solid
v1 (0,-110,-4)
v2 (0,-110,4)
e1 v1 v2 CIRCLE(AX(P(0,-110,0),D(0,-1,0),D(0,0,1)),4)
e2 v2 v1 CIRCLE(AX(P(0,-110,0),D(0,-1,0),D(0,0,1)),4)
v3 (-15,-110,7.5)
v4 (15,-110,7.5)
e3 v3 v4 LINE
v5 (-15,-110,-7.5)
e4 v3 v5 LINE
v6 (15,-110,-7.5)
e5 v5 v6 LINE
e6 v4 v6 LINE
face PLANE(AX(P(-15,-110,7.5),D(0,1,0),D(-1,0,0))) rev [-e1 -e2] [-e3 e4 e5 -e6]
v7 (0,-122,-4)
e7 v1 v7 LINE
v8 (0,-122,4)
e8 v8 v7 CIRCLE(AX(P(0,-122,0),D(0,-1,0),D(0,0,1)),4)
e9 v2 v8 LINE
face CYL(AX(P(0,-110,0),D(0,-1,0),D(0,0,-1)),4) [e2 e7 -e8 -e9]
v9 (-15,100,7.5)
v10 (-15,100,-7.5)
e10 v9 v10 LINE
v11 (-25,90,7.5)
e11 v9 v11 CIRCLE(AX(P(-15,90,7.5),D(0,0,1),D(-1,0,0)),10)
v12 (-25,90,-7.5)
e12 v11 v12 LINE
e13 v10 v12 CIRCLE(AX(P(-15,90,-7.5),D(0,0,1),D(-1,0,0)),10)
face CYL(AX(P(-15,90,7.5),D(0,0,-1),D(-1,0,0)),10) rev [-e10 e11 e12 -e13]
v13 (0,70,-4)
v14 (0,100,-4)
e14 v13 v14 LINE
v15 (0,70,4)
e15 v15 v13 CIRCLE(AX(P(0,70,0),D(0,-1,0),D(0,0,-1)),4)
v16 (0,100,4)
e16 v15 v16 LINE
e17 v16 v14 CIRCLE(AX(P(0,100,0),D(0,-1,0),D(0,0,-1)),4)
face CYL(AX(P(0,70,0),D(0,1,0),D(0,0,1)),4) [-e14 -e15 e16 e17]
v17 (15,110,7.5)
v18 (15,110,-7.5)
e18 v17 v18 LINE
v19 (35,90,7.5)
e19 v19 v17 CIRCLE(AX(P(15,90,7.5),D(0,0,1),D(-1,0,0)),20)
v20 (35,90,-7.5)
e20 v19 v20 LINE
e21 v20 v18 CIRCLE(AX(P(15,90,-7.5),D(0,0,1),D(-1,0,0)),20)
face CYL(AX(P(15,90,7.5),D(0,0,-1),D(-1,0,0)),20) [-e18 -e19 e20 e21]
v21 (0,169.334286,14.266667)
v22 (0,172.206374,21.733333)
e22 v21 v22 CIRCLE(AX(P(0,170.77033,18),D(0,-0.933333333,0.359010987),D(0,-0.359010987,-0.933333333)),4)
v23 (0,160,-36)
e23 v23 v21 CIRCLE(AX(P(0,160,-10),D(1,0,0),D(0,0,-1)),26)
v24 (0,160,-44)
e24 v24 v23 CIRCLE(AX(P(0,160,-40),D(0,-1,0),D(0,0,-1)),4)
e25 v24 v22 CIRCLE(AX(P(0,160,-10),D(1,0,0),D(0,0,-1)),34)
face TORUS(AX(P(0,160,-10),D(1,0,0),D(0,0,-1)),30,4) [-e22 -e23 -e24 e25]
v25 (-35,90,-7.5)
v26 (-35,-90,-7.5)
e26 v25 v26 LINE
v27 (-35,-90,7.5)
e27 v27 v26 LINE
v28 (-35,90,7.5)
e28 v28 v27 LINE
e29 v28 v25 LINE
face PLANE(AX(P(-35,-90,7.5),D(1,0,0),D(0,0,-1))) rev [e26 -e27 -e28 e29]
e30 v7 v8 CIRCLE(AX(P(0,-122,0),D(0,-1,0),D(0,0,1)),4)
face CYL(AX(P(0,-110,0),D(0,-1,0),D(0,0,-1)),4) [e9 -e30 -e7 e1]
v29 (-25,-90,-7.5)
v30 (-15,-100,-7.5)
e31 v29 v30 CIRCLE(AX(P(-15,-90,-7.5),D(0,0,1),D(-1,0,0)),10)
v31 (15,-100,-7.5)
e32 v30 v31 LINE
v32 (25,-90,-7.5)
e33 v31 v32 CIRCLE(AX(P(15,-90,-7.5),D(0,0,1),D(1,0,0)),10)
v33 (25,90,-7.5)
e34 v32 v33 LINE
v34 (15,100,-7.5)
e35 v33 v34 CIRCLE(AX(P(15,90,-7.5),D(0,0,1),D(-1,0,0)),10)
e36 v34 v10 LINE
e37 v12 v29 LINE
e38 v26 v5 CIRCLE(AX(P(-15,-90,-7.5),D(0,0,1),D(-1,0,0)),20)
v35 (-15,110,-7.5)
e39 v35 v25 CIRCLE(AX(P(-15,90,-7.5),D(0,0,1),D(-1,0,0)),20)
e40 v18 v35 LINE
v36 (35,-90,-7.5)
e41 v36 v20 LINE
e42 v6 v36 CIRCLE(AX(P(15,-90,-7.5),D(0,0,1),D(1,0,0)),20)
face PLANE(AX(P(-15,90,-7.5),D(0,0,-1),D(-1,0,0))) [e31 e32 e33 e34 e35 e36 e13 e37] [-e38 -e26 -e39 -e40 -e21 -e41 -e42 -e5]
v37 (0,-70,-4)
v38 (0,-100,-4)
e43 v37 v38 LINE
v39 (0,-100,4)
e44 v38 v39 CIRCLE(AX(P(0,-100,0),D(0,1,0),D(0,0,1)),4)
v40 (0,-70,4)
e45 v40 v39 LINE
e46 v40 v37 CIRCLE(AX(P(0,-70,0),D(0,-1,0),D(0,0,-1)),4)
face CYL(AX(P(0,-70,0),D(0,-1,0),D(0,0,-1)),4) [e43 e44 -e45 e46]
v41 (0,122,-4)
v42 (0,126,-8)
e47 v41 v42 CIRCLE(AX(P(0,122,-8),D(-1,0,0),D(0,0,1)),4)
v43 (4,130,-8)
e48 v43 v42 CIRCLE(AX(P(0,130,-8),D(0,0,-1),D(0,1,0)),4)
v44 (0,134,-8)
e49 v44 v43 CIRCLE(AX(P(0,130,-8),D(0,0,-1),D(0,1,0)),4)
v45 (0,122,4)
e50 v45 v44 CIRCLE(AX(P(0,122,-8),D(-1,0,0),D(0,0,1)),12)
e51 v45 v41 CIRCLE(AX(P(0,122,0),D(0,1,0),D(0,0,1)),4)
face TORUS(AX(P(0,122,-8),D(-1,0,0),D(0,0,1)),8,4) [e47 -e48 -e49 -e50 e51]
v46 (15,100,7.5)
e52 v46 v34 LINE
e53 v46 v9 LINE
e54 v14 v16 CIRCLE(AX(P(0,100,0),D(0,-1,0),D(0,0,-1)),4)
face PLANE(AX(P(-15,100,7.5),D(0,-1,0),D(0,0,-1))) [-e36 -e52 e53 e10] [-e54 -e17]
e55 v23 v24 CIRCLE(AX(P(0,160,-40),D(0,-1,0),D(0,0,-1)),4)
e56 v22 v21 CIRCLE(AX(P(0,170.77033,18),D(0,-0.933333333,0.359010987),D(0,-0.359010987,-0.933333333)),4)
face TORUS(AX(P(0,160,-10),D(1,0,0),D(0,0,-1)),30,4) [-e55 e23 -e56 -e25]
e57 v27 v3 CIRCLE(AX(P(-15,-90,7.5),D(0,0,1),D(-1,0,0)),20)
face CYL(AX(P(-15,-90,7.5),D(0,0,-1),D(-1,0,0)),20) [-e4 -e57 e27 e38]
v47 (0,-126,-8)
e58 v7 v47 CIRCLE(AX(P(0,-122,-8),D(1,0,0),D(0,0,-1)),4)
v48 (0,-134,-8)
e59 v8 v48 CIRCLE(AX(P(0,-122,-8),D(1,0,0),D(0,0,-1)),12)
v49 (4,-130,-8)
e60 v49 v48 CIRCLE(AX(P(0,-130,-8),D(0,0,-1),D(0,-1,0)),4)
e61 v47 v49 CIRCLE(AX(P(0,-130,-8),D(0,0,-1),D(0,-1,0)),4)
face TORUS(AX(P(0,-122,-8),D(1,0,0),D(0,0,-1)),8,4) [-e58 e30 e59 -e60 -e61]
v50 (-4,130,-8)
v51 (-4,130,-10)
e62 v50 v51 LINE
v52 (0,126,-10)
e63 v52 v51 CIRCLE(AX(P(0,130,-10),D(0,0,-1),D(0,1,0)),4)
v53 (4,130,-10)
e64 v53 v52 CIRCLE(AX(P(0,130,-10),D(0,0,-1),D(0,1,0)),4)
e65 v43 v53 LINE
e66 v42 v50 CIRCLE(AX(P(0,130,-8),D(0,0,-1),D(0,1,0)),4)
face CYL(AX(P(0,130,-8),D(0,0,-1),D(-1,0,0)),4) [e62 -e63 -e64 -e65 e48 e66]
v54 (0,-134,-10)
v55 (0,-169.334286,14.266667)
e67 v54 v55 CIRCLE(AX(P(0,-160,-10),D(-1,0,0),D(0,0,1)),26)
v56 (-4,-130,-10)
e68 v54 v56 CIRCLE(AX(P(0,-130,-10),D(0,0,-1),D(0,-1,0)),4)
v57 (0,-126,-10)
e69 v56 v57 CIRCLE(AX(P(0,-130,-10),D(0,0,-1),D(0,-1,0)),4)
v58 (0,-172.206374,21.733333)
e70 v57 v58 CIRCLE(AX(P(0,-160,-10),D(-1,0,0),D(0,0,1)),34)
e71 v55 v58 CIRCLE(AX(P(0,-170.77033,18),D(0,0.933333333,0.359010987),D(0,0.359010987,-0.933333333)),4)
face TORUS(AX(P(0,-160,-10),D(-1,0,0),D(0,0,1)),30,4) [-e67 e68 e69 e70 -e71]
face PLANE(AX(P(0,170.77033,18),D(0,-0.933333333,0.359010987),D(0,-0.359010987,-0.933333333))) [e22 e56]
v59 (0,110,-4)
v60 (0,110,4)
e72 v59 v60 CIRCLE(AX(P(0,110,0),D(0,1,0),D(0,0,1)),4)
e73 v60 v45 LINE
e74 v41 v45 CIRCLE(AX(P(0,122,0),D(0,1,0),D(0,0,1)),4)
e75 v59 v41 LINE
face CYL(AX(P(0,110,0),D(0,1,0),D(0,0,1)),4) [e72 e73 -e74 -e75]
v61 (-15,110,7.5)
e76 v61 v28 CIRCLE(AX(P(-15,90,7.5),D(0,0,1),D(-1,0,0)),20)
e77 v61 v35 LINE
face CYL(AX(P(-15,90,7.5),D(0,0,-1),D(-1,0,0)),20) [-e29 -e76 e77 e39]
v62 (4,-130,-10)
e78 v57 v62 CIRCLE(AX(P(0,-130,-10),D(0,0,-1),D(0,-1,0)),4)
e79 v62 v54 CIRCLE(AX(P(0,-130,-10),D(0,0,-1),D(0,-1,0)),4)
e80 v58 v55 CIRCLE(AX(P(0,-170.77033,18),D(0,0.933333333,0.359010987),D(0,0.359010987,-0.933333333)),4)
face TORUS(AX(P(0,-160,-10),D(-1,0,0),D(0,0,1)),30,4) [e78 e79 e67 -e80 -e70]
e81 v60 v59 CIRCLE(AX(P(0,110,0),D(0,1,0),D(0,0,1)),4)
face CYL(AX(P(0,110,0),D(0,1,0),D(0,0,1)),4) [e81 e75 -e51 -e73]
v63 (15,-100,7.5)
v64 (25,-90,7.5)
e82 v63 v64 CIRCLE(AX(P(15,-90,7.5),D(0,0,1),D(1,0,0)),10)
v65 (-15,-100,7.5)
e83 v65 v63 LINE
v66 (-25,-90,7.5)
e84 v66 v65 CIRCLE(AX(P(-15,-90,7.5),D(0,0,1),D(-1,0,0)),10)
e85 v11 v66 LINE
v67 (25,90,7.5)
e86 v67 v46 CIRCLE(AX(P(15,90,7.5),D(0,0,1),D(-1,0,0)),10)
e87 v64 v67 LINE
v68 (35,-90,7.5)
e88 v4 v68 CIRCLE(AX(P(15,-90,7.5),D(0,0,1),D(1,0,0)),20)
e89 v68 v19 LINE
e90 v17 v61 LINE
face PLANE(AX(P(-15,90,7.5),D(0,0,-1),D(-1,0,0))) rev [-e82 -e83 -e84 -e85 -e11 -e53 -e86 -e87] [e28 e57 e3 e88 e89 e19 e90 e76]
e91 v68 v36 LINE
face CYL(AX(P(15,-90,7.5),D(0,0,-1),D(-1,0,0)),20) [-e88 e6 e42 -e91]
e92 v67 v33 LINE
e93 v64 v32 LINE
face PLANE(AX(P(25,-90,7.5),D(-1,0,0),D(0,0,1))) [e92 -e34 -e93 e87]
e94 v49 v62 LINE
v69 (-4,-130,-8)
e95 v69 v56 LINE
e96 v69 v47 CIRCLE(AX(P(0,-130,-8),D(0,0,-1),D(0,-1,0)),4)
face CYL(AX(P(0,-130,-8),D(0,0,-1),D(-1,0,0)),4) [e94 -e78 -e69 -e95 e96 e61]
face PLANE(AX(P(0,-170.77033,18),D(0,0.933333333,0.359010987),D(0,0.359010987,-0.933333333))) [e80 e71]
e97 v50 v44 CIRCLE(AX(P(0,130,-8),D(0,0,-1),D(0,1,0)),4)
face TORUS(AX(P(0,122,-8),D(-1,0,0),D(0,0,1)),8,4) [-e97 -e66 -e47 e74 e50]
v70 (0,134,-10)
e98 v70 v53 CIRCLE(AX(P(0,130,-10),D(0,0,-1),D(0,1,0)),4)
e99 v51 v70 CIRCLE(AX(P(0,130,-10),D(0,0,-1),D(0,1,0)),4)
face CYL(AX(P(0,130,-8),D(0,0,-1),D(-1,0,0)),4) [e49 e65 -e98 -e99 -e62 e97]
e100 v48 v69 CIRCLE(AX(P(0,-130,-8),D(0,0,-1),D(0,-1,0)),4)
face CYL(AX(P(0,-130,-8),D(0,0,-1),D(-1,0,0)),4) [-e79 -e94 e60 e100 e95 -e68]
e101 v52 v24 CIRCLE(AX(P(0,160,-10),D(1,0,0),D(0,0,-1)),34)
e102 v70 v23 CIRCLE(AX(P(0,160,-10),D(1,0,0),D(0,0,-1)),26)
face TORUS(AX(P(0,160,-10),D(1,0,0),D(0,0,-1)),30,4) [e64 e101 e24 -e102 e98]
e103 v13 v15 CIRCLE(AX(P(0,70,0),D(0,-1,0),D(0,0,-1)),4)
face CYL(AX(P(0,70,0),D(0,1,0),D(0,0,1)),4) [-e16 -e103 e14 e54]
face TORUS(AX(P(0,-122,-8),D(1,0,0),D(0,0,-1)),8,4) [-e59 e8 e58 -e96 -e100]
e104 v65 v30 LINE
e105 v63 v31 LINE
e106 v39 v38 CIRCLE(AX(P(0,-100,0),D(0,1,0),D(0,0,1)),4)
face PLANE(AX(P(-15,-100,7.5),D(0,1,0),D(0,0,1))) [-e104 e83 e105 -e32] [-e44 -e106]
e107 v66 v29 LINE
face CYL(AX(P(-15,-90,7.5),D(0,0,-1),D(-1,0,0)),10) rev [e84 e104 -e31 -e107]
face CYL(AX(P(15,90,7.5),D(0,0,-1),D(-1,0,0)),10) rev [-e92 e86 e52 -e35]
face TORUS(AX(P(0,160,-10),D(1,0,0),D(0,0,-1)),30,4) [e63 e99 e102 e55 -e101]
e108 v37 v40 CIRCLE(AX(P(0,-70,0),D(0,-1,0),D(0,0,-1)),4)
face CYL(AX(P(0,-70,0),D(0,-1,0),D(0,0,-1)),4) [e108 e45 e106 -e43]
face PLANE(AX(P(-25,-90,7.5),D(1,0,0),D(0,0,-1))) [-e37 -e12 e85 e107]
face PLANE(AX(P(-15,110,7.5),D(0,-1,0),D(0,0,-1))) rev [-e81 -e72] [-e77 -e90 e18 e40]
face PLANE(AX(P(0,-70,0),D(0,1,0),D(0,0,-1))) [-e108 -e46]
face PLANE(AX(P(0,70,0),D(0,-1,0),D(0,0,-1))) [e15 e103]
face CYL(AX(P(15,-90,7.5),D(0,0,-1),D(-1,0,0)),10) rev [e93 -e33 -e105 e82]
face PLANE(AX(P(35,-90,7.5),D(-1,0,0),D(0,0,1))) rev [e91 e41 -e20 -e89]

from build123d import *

# Parameters (mm, degrees)
EXTRUDE_1_DEPTH = 7.5
SKETCH_6_R      = 4
SKETCH_7_R      = 4
EXTRUDE_2_DEPTH = 30


with BuildPart() as part:
    # 草图4 → 凸台-拉伸1 (new, symmetric)
    with BuildSketch(Plane.XY):
        with BuildLine():
            Line((-15, 110), (15, 110))
            ThreePointArc((15, 110), (29.142135624, 104.142135624), (35, 90))
            Line((35, 90), (35, -90))
            ThreePointArc((35, -90), (29.142135624, -104.142135624), (15, -110))
            Line((15, -110), (-15, -110))
            ThreePointArc((-15, -110), (-29.142135624, -104.142135624), (-35, -90))
            Line((-35, -90), (-35, 90))
            ThreePointArc((-35, 90), (-29.142135624, 104.142135624), (-15, 110))
        make_face()
        with BuildLine():
            Line((-15, -100), (15, -100))
            ThreePointArc((15, -100), (22.071067812, -97.071067812), (25, -90))
            Line((25, -90), (25, 90))
            ThreePointArc((25, 90), (22.071067812, 97.071067812), (15, 100))
            Line((15, 100), (-15, 100))
            ThreePointArc((-15, 100), (-22.071067812, 97.071067812), (-25, 90))
            Line((-25, 90), (-25, -90))
            ThreePointArc((-25, -90), (-22.071067812, -97.071067812), (-15, -100))
        make_face(mode=Mode.SUBTRACT)
    extrude(amount=EXTRUDE_1_DEPTH, both=True)

    # 扫描1: sweep along a path in 草图5
    with BuildLine(Plane(origin=(0, 0, 0), x_dir=(0, 0, -1), z_dir=(1, 0, 0))) as sweep_1_path:
        Line((0, 110), (0, 122))
        ThreePointArc((0, 122), (2.343145751, 127.656854249), (8, 130))
        Line((8, 130), (10, 130))
        ThreePointArc((10, 130), (34.729636961, 176.983670268), (-18, 170.770329614))
    # 草图6 → 扫描1 (sweep)
    with BuildSketch(Plane(origin=(0, 110, 0), x_dir=(1, 0, 0), z_dir=(0, 1, 0))):
        Circle(SKETCH_6_R)
    sweep_1 = sweep(path=sweep_1_path.line)

    # 草图7 → 凸台-拉伸2 (add)
    with BuildSketch(Plane.XZ.offset(-100)):
        with Locations(Location((0, 0, 0), (0, 0, 90))):
            Circle(SKETCH_7_R)
    extrude_2 = extrude(amount=EXTRUDE_2_DEPTH)

    # 镜向1: 扫描1, 凸台-拉伸2 across plane
    add(sweep_1.mirror(Plane.ZX))
    add(extrude_2.mirror(Plane.ZX))


solid = part.part
